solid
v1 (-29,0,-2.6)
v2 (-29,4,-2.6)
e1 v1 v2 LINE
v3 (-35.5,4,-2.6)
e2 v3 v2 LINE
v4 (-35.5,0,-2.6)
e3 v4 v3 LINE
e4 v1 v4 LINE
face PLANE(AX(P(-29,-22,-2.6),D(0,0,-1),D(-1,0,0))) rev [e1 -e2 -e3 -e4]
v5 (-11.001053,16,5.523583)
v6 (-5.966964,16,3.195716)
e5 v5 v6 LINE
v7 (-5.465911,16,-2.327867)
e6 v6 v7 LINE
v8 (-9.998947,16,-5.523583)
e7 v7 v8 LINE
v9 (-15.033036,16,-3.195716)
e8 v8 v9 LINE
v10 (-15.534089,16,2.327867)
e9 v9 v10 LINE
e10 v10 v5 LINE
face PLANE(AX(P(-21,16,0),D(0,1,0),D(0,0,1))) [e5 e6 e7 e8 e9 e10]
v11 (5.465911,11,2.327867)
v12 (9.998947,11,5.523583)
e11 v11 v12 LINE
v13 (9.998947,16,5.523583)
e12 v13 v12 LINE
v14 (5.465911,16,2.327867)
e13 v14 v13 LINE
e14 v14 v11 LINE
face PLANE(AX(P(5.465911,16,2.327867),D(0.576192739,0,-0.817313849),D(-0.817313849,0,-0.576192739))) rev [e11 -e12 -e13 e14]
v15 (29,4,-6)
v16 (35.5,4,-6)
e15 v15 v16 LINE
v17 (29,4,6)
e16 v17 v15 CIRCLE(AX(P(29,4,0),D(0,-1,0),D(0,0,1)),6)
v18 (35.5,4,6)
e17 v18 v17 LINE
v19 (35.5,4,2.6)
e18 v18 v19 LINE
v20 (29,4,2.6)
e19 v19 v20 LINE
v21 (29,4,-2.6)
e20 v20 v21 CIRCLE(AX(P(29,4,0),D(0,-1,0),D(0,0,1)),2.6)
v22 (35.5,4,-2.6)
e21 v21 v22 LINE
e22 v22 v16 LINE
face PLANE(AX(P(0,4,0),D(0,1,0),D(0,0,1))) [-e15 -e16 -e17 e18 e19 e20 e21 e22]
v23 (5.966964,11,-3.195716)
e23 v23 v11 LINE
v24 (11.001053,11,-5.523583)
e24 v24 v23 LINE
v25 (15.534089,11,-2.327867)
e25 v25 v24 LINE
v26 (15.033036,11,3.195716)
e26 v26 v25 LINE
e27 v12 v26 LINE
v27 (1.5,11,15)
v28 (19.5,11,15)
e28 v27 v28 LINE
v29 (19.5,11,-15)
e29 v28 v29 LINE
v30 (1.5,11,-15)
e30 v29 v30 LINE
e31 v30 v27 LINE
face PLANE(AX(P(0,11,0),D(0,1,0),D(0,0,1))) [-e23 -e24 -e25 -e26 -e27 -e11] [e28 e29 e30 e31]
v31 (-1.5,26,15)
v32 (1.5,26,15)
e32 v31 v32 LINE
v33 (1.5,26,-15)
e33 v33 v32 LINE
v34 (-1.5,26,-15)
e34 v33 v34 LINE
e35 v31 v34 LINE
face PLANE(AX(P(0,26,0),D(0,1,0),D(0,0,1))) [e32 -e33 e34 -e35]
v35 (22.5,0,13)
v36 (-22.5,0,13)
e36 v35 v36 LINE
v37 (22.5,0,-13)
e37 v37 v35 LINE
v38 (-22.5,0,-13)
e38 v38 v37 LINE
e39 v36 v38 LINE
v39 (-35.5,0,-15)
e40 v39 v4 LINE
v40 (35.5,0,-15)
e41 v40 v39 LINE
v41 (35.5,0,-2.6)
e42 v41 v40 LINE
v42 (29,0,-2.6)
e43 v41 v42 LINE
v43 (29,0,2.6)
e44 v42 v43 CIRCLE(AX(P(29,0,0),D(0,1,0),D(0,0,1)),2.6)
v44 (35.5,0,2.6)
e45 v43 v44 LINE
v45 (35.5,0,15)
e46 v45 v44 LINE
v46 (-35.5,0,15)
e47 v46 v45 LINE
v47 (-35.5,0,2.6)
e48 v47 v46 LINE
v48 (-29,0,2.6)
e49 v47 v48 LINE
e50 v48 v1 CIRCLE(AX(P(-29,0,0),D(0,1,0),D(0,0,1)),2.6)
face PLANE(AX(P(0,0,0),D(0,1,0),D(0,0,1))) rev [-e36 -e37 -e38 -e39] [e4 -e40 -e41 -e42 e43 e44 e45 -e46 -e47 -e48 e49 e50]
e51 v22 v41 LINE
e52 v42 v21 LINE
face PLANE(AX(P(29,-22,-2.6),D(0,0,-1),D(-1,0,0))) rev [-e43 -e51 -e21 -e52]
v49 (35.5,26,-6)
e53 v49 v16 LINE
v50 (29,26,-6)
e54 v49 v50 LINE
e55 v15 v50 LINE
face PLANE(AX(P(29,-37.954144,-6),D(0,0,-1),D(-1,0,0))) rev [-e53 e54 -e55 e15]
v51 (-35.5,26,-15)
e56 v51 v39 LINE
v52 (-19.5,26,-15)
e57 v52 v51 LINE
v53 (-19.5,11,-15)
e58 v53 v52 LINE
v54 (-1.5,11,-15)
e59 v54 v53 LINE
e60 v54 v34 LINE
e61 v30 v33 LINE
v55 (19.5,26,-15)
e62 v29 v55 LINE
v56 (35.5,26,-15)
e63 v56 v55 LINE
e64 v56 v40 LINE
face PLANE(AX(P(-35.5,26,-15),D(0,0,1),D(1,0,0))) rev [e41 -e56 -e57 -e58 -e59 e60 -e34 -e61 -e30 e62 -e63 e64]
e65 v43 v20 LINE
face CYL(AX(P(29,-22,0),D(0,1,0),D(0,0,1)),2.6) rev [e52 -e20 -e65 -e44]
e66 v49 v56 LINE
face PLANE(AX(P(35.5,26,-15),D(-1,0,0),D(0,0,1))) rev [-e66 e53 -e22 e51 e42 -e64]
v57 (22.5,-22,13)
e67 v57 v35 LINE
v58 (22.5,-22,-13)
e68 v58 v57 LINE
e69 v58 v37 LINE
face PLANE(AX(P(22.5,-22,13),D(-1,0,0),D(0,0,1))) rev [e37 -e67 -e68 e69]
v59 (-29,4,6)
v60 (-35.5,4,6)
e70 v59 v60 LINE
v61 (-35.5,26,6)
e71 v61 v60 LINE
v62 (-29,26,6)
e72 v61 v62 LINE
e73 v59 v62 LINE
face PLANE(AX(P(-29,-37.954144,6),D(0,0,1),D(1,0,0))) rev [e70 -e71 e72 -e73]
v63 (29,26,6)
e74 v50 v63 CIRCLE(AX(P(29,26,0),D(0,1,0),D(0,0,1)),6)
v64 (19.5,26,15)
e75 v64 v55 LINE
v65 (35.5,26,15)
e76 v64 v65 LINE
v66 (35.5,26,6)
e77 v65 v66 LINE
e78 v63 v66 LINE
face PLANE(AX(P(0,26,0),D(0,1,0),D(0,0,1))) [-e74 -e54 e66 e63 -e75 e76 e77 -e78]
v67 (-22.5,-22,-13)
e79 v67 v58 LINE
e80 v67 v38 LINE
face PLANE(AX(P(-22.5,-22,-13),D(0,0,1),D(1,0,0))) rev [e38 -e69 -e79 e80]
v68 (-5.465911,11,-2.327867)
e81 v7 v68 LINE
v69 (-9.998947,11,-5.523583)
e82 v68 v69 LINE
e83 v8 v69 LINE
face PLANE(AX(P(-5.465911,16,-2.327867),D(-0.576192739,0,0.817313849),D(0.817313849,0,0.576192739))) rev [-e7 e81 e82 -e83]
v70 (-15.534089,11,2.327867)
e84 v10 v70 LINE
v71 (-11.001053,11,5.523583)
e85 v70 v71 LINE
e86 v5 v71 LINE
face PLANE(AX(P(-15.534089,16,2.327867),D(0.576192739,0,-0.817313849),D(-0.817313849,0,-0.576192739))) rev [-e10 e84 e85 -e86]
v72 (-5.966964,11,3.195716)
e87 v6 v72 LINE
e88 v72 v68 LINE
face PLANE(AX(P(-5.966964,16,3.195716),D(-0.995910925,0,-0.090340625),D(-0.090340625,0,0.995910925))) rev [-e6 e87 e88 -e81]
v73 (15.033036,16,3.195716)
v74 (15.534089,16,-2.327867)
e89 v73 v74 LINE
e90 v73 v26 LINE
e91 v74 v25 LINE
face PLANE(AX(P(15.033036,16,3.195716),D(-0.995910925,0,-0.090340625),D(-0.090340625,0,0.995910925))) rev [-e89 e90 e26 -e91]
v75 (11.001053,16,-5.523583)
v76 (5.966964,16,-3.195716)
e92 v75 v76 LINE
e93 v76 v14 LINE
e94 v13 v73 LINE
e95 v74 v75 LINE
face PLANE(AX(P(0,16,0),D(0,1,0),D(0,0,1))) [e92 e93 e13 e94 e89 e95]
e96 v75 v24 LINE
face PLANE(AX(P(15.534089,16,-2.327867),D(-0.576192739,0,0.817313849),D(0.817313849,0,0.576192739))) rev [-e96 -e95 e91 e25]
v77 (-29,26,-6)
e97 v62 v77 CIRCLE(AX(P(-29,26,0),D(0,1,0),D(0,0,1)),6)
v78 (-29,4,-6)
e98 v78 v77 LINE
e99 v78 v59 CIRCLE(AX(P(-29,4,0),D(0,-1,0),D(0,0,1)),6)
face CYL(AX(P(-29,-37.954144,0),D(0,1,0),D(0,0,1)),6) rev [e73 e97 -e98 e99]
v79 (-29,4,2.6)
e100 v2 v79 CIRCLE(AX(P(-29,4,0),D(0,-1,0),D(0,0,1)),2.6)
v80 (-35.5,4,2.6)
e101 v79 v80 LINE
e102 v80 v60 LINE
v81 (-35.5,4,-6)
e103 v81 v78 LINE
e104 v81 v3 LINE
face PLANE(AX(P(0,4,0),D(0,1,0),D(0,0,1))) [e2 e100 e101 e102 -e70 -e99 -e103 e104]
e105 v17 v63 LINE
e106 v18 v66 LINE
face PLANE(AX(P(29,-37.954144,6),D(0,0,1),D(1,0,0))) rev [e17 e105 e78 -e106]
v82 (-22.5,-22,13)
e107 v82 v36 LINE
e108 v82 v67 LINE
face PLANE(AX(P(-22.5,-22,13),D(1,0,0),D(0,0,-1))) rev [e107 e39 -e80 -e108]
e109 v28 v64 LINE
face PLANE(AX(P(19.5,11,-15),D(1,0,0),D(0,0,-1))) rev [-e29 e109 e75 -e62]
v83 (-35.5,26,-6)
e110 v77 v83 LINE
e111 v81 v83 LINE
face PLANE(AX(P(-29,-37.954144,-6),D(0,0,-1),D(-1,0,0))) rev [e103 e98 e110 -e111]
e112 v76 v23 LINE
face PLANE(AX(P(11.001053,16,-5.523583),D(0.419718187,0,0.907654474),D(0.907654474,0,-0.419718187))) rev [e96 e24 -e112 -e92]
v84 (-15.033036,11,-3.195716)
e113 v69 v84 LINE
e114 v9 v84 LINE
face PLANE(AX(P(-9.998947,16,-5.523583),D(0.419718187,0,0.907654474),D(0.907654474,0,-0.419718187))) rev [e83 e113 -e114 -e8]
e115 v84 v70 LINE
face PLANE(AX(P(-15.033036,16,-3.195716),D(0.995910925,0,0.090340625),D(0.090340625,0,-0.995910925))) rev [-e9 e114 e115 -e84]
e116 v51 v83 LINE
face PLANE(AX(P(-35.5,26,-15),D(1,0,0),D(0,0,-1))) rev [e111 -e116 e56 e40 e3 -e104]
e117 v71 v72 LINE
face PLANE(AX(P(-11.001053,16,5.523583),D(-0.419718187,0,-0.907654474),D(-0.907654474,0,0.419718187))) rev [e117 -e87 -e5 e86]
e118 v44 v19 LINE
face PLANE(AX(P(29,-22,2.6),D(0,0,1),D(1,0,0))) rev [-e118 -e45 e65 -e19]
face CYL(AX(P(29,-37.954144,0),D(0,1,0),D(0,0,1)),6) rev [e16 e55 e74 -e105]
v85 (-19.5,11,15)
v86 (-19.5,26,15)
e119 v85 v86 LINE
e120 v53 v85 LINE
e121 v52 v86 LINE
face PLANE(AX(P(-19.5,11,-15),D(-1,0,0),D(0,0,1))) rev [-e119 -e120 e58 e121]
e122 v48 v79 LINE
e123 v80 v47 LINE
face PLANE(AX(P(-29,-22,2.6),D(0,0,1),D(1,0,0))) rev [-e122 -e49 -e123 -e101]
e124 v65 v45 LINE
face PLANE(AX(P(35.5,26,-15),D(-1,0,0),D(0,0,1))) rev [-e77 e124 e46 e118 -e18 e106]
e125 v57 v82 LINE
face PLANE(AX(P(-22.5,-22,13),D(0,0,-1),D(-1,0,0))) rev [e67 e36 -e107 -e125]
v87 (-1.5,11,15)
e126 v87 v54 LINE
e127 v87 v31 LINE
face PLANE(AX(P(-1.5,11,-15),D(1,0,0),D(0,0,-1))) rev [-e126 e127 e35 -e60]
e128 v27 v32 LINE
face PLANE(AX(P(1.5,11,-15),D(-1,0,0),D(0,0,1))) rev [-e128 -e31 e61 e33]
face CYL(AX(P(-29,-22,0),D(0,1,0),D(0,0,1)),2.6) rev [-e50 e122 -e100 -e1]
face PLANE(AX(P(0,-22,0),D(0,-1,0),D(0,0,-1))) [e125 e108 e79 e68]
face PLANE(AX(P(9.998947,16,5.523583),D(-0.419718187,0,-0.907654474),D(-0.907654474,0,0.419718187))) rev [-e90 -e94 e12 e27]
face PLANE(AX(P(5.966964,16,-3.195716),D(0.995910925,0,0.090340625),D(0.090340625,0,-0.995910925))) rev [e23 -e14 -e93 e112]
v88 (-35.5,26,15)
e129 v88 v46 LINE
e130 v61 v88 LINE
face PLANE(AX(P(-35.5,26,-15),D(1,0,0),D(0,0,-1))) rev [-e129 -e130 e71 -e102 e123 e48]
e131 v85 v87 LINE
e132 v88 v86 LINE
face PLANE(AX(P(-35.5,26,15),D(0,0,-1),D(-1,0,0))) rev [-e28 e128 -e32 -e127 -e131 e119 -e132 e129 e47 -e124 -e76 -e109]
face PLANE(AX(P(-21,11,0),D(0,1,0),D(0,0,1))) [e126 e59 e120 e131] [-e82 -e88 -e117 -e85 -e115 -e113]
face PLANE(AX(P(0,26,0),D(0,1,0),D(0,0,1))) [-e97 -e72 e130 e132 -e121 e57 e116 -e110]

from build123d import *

# Parameters (mm, degrees)
SKETCH_1_W             = 71
SKETCH_1_H             = 30
EXTRUDE_1_DEPTH        = 26
SKETCH_2_W             = 45
SKETCH_2_H             = 26
EXTRUDE_2_DEPTH        = 22
CUT_EXTRUDE_1_DEPTH    = 62.556884262
CUT_EXTRUDE_2_DEPTH    = 22
SKETCH_5_W             = 18
SKETCH_5_H             = 30
CUT_EXTRUDE_3_DEPTH    = 15
PATTERN_LINEAR_1_COUNT = 2
PATTERN_LINEAR_1_PITCH = 21
EXTRUDE_3_DEPTH        = 5
PATTERN_LINEAR_2_COUNT = 2
PATTERN_LINEAR_2_PITCH = 21


with BuildPart() as part:
    # 草图1 → 凸台-拉伸1 (new body)
    with BuildSketch(Plane(origin=(0, 0, 0), x_dir=(1, 0, 0), z_dir=(0, 1, 0))):
        Rectangle(SKETCH_1_W, SKETCH_1_H)
    extrude(amount=EXTRUDE_1_DEPTH)

    # 草图2 → 凸台-拉伸2 (add)
    with BuildSketch(Plane.XZ):
        Rectangle(SKETCH_2_W, SKETCH_2_H)
    extrude(amount=EXTRUDE_2_DEPTH)

    # 草图3 → 切除-拉伸1 (cut, through all)
    with BuildSketch(Plane(origin=(0, 26, 0), x_dir=(1, 0, 0), z_dir=(0, 1, 0))):
        with BuildLine():
            Line((-29, -2.6), (-61.70015948, -2.6))
            ThreePointArc((-61.70015948, -2.6), (-64.30015948, 0), (-61.70015948, 2.6))
            Line((-61.70015948, 2.6), (-29, 2.6))
            ThreePointArc((-29, 2.6), (-26.4, 0), (-29, -2.6))
        make_face()
        with BuildLine():
            Line((29, 2.6), (61.70015948, 2.6))
            ThreePointArc((61.70015948, 2.6), (64.30015948, 0), (61.70015948, -2.6))
            Line((61.70015948, -2.6), (29, -2.6))
            ThreePointArc((29, -2.6), (26.4, 0), (29, 2.6))
        make_face()
    extrude(amount=-CUT_EXTRUDE_1_DEPTH, mode=Mode.SUBTRACT)

    # 草图4 → 切除-拉伸2 (cut)
    with BuildSketch(Plane(origin=(0, 26, 0), x_dir=(1, 0, 0), z_dir=(0, 1, 0))):
        with BuildLine():
            Line((29, 6), (52.513840992, 6))
            ThreePointArc((52.513840992, 6), (58.513840992, 0), (52.513840992, -6))
            Line((52.513840992, -6), (29, -6))
            ThreePointArc((29, -6), (23, 0), (29, 6))
        make_face()
        with BuildLine():
            Line((-29, -6), (-53.007180335, -6))
            ThreePointArc((-53.007180335, -6), (-59.007180335, 0), (-53.007180335, 6))
            Line((-53.007180335, 6), (-29, 6))
            ThreePointArc((-29, 6), (-23, 0), (-29, -6))
        make_face()
    extrude(amount=-CUT_EXTRUDE_2_DEPTH, mode=Mode.SUBTRACT)

    # 草图5 → 切除-拉伸3 (cut)
    with BuildSketch(Plane(origin=(0, 26, 0), x_dir=(1, 0, 0), z_dir=(0, 1, 0))):
        with Locations((10.5, 0)):
            Rectangle(SKETCH_5_W, SKETCH_5_H)
    cut_extrude_3 = extrude(amount=-CUT_EXTRUDE_3_DEPTH, mode=Mode.SUBTRACT)

    # 阵列(线性)1: 切除-拉伸3 ×2
    with Locations(*[(-i * PATTERN_LINEAR_1_PITCH, 0, 0) for i in range(1, PATTERN_LINEAR_1_COUNT)]):
        add(cut_extrude_3, mode=Mode.SUBTRACT)

    # 草图6 → 凸台-拉伸3 (add)
    with BuildSketch(Plane(origin=(0, 11, 0), x_dir=(1, 0, 0), z_dir=(0, 1, 0))):
        Polygon((15.033036482, -3.195715708), (15.534089227, 2.327866896), (11.001052745, 5.523582603), (5.966963518, 3.195715708), (5.465910773, -2.327866896), (9.998947255, -5.523582603), align=None)
    extrude_3 = extrude(amount=EXTRUDE_3_DEPTH)

    # 阵列(线性)2: 凸台-拉伸3 ×2
    with Locations(*[(-i * PATTERN_LINEAR_2_PITCH, 0, 0) for i in range(1, PATTERN_LINEAR_2_COUNT)]):
        add(extrude_3)


solid = part.part
